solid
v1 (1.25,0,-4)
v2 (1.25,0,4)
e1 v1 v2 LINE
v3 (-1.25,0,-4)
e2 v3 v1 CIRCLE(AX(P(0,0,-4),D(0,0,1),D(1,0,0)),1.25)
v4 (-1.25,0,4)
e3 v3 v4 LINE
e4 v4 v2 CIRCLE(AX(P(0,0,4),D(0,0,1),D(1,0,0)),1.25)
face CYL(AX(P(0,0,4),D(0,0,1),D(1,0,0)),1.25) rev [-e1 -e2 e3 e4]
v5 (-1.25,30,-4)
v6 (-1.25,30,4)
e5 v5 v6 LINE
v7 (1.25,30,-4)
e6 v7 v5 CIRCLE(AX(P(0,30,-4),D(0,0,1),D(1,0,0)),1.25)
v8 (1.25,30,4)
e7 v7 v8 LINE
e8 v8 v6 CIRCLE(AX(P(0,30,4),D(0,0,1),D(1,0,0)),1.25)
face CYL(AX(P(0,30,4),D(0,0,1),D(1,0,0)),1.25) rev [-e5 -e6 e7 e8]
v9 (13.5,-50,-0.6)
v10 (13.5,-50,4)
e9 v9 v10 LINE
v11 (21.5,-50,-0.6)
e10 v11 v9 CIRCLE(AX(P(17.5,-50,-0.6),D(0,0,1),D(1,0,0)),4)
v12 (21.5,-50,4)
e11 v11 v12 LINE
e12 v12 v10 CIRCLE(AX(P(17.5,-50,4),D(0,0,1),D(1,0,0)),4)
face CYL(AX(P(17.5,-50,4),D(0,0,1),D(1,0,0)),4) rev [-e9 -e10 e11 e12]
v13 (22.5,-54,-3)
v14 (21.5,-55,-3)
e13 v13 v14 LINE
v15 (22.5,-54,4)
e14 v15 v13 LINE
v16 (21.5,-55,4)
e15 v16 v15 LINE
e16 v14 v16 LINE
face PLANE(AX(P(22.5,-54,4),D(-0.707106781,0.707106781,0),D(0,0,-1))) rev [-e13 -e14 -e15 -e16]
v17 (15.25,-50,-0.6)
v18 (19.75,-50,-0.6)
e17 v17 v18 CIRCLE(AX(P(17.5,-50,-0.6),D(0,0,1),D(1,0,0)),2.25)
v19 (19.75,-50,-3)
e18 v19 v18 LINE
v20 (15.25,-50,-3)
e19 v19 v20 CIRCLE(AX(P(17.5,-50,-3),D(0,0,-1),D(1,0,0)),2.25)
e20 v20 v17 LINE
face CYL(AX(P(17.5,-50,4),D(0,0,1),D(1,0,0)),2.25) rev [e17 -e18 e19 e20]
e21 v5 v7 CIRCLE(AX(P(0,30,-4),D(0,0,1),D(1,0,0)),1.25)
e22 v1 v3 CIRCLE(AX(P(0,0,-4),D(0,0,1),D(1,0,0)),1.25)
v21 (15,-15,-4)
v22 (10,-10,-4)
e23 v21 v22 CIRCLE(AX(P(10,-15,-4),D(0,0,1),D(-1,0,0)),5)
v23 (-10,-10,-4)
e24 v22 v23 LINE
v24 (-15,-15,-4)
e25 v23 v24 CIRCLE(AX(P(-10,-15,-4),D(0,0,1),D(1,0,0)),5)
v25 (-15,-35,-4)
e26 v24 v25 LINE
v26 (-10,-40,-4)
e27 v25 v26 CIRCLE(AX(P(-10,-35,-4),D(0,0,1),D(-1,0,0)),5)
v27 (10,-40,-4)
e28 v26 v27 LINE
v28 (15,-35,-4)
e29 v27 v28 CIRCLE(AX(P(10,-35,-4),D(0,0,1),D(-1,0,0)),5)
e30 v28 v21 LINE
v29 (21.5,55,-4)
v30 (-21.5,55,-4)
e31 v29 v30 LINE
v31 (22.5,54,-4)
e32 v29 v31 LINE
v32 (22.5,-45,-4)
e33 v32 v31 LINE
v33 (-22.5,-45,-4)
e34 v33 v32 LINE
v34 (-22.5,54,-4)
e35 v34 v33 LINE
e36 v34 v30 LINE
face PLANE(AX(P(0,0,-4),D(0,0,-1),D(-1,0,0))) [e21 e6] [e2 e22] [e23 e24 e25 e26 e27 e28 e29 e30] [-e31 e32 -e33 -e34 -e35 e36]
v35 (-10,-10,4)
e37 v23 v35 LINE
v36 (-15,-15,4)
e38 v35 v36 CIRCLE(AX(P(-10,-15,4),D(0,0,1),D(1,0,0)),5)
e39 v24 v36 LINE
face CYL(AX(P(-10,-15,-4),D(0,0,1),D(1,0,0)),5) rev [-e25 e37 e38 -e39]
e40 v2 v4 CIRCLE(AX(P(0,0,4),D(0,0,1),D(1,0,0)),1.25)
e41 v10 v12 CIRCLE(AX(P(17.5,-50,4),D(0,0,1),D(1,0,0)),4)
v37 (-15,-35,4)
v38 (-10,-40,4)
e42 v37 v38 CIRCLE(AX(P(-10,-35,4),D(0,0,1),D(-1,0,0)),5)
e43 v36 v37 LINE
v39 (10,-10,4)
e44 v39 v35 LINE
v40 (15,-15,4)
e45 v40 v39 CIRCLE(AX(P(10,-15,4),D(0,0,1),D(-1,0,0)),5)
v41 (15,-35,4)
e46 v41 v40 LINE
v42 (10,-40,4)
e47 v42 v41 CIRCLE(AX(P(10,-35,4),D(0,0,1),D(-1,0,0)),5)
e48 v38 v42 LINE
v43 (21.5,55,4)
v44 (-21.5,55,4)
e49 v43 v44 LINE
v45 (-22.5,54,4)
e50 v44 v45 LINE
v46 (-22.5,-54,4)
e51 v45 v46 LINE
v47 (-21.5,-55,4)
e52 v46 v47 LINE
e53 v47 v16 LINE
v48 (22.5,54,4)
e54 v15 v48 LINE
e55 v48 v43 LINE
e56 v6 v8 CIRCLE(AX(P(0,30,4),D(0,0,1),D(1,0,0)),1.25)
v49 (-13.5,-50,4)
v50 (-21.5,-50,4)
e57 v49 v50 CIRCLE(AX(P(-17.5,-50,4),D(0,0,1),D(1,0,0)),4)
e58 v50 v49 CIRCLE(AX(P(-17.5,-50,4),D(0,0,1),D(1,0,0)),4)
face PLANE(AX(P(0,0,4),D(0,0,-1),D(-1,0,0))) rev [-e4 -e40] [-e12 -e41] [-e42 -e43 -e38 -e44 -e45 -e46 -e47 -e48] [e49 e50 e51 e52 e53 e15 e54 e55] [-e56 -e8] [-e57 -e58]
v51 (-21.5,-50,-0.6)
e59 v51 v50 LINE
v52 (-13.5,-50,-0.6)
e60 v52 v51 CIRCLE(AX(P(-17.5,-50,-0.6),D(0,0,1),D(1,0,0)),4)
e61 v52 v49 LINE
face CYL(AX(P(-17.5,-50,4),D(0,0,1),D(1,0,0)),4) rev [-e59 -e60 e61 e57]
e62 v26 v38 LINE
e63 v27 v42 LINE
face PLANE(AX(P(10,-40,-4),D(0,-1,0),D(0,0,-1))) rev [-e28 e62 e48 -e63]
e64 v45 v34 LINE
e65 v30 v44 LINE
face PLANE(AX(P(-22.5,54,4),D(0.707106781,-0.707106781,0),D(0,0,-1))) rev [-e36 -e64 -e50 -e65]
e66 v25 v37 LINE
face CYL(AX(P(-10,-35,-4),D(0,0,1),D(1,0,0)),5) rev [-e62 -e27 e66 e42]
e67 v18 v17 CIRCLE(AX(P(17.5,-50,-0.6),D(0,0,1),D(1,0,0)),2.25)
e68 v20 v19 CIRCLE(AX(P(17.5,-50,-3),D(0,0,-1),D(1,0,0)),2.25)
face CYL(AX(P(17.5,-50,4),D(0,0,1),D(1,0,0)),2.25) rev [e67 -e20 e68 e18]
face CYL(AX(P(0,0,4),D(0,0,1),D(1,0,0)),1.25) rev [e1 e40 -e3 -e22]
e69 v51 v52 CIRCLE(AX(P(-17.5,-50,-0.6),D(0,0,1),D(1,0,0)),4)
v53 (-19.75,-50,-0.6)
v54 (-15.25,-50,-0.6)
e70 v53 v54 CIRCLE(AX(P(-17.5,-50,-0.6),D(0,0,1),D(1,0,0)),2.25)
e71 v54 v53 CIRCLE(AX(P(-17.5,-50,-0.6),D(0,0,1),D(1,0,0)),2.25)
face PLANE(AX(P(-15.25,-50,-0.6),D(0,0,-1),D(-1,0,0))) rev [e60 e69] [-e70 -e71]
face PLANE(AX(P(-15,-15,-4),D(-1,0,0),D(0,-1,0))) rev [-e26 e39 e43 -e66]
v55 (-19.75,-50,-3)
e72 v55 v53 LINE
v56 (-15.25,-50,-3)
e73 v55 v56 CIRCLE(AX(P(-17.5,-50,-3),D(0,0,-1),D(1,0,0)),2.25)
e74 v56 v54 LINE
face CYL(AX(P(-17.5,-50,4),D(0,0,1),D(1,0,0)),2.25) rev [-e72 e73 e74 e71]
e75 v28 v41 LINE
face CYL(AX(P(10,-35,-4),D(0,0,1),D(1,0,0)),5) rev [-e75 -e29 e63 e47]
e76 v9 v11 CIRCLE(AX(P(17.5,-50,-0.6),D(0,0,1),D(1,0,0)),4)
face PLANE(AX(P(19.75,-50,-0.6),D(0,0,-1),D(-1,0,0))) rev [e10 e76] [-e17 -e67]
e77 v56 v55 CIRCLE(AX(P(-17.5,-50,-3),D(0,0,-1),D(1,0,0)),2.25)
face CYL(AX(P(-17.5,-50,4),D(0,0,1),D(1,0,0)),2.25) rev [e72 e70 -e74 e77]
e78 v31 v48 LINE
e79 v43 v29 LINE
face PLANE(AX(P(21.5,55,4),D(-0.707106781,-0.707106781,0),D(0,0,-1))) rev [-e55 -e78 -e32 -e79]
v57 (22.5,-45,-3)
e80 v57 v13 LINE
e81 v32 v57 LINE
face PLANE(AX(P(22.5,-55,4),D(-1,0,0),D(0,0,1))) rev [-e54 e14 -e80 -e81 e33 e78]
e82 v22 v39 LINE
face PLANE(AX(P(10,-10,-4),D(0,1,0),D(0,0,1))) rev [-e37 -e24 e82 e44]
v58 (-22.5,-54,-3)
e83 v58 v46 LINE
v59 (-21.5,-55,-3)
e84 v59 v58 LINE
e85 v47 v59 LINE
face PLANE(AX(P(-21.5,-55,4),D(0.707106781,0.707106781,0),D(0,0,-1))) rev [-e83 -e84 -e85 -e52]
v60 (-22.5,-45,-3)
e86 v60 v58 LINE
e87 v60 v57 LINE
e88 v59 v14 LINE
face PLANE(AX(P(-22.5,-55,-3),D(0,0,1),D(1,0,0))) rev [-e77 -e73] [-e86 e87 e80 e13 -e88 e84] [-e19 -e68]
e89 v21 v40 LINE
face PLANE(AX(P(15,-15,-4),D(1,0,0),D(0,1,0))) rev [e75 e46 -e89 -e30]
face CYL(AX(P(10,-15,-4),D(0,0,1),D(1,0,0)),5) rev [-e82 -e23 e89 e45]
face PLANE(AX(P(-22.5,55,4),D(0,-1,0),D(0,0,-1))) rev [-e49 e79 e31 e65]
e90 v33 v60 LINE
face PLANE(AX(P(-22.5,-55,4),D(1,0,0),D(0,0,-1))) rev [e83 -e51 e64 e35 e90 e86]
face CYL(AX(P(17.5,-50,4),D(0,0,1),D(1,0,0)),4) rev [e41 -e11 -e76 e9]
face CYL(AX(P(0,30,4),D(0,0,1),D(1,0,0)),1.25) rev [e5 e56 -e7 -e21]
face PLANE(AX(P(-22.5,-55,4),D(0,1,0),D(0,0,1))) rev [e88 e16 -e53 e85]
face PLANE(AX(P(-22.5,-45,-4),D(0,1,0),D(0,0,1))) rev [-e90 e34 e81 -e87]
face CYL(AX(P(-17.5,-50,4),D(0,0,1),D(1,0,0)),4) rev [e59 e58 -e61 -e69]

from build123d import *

# Parameters (mm, degrees)
SKETCH1_W                                          = 45
SKETCH1_H                                          = 110
BOSS_EXTRUDE1_DEPTH                                = 4
HOLE_SIZE_BASED_ON_SOCKET_HEAD_CAP_SCR_D           = 4.5
HOLE_SIZE_BASED_ON_SOCKET_HEAD_CAP_SCR_DEPTH       = 12.4
HOLE_SIZE_BASED_ON_SOCKET_HEAD_CAP_SCR_CBORE_D     = 8
HOLE_SIZE_BASED_ON_SOCKET_HEAD_CAP_SCR_CBORE_DEPTH = 4.6
HOLE_SIZE_BASED_ON_SOCKET_HEAD_CAP_SCR_TIP         = 1.351936393
SKETCH4_W                                          = 1
SKETCH4_H                                          = 10
CUT_EXTRUDE1_DEPTH                                 = 72.175838597
M3_TAPPED_HOLE1_D                                  = 2.5
CHAMFER1_SIZE                                      = 1
CUT_EXTRUDE2_DEPTH                                 = 60.960403601


with BuildPart() as part:
    # Sketch1 → Boss-Extrude1 (new, symmetric)
    with BuildSketch(Plane.XY):
        Rectangle(SKETCH1_W, SKETCH1_H)
    extrude(amount=BOSS_EXTRUDE1_DEPTH, both=True)

    # Hole size (% based on socket head cap screw type)1
    with Locations(Plane.XY.offset(4)):
        with Locations((-17.5, -50), (17.5, -50)):
            CounterBoreHole(HOLE_SIZE_BASED_ON_SOCKET_HEAD_CAP_SCR_D / 2, HOLE_SIZE_BASED_ON_SOCKET_HEAD_CAP_SCR_CBORE_D / 2, HOLE_SIZE_BASED_ON_SOCKET_HEAD_CAP_SCR_CBORE_DEPTH, depth=HOLE_SIZE_BASED_ON_SOCKET_HEAD_CAP_SCR_DEPTH)
            with Locations((0, 0, -(HOLE_SIZE_BASED_ON_SOCKET_HEAD_CAP_SCR_DEPTH + HOLE_SIZE_BASED_ON_SOCKET_HEAD_CAP_SCR_TIP / 2))):  # 118° drill point
                Cone(0, HOLE_SIZE_BASED_ON_SOCKET_HEAD_CAP_SCR_D / 2, HOLE_SIZE_BASED_ON_SOCKET_HEAD_CAP_SCR_TIP, mode=Mode.SUBTRACT)

    # Sketch4 → Cut-Extrude1 (cut, through all)
    with BuildSketch(Plane(origin=(22.5, 0, 0), x_dir=(0, 0, -1), z_dir=(1, 0, 0))):
        with Locations((3.5, -50)):
            Rectangle(SKETCH4_W, SKETCH4_H)
    extrude(amount=-CUT_EXTRUDE1_DEPTH, mode=Mode.SUBTRACT)

    # M3 Tapped Hole1 (through all)
    with Locations(Plane.XY.offset(4)):
        with Locations((0, 30), (0, 0)):
            Hole(M3_TAPPED_HOLE1_D / 2)

    # Chamfer1
    chamfer1_edges = [part.edges().sort_by_distance(p)[0] for p in [
        (22.5, -55, 0.5),
        (-22.5, -55, 0.5),
        (-22.5, 55, 0),
        (22.5, 55, 0),
    ]]
    chamfer(chamfer1_edges, length=CHAMFER1_SIZE)

    # Sketch7 → Cut-Extrude2 (cut, through all)
    with BuildSketch(Plane.XY.offset(4)):
        with BuildLine():
            Line((10, -10), (-10, -10))
            ThreePointArc((-10, -10), (-13.535533906, -11.464466094), (-15, -15))
            Line((-15, -15), (-15, -35))
            ThreePointArc((-15, -35), (-13.535533906, -38.535533906), (-10, -40))
            Line((-10, -40), (10, -40))
            ThreePointArc((10, -40), (13.535533906, -38.535533906), (15, -35))
            Line((15, -35), (15, -15))
            ThreePointArc((15, -15), (13.535533906, -11.464466094), (10, -10))
        make_face()
    extrude(amount=-CUT_EXTRUDE2_DEPTH, mode=Mode.SUBTRACT)


solid = part.part
